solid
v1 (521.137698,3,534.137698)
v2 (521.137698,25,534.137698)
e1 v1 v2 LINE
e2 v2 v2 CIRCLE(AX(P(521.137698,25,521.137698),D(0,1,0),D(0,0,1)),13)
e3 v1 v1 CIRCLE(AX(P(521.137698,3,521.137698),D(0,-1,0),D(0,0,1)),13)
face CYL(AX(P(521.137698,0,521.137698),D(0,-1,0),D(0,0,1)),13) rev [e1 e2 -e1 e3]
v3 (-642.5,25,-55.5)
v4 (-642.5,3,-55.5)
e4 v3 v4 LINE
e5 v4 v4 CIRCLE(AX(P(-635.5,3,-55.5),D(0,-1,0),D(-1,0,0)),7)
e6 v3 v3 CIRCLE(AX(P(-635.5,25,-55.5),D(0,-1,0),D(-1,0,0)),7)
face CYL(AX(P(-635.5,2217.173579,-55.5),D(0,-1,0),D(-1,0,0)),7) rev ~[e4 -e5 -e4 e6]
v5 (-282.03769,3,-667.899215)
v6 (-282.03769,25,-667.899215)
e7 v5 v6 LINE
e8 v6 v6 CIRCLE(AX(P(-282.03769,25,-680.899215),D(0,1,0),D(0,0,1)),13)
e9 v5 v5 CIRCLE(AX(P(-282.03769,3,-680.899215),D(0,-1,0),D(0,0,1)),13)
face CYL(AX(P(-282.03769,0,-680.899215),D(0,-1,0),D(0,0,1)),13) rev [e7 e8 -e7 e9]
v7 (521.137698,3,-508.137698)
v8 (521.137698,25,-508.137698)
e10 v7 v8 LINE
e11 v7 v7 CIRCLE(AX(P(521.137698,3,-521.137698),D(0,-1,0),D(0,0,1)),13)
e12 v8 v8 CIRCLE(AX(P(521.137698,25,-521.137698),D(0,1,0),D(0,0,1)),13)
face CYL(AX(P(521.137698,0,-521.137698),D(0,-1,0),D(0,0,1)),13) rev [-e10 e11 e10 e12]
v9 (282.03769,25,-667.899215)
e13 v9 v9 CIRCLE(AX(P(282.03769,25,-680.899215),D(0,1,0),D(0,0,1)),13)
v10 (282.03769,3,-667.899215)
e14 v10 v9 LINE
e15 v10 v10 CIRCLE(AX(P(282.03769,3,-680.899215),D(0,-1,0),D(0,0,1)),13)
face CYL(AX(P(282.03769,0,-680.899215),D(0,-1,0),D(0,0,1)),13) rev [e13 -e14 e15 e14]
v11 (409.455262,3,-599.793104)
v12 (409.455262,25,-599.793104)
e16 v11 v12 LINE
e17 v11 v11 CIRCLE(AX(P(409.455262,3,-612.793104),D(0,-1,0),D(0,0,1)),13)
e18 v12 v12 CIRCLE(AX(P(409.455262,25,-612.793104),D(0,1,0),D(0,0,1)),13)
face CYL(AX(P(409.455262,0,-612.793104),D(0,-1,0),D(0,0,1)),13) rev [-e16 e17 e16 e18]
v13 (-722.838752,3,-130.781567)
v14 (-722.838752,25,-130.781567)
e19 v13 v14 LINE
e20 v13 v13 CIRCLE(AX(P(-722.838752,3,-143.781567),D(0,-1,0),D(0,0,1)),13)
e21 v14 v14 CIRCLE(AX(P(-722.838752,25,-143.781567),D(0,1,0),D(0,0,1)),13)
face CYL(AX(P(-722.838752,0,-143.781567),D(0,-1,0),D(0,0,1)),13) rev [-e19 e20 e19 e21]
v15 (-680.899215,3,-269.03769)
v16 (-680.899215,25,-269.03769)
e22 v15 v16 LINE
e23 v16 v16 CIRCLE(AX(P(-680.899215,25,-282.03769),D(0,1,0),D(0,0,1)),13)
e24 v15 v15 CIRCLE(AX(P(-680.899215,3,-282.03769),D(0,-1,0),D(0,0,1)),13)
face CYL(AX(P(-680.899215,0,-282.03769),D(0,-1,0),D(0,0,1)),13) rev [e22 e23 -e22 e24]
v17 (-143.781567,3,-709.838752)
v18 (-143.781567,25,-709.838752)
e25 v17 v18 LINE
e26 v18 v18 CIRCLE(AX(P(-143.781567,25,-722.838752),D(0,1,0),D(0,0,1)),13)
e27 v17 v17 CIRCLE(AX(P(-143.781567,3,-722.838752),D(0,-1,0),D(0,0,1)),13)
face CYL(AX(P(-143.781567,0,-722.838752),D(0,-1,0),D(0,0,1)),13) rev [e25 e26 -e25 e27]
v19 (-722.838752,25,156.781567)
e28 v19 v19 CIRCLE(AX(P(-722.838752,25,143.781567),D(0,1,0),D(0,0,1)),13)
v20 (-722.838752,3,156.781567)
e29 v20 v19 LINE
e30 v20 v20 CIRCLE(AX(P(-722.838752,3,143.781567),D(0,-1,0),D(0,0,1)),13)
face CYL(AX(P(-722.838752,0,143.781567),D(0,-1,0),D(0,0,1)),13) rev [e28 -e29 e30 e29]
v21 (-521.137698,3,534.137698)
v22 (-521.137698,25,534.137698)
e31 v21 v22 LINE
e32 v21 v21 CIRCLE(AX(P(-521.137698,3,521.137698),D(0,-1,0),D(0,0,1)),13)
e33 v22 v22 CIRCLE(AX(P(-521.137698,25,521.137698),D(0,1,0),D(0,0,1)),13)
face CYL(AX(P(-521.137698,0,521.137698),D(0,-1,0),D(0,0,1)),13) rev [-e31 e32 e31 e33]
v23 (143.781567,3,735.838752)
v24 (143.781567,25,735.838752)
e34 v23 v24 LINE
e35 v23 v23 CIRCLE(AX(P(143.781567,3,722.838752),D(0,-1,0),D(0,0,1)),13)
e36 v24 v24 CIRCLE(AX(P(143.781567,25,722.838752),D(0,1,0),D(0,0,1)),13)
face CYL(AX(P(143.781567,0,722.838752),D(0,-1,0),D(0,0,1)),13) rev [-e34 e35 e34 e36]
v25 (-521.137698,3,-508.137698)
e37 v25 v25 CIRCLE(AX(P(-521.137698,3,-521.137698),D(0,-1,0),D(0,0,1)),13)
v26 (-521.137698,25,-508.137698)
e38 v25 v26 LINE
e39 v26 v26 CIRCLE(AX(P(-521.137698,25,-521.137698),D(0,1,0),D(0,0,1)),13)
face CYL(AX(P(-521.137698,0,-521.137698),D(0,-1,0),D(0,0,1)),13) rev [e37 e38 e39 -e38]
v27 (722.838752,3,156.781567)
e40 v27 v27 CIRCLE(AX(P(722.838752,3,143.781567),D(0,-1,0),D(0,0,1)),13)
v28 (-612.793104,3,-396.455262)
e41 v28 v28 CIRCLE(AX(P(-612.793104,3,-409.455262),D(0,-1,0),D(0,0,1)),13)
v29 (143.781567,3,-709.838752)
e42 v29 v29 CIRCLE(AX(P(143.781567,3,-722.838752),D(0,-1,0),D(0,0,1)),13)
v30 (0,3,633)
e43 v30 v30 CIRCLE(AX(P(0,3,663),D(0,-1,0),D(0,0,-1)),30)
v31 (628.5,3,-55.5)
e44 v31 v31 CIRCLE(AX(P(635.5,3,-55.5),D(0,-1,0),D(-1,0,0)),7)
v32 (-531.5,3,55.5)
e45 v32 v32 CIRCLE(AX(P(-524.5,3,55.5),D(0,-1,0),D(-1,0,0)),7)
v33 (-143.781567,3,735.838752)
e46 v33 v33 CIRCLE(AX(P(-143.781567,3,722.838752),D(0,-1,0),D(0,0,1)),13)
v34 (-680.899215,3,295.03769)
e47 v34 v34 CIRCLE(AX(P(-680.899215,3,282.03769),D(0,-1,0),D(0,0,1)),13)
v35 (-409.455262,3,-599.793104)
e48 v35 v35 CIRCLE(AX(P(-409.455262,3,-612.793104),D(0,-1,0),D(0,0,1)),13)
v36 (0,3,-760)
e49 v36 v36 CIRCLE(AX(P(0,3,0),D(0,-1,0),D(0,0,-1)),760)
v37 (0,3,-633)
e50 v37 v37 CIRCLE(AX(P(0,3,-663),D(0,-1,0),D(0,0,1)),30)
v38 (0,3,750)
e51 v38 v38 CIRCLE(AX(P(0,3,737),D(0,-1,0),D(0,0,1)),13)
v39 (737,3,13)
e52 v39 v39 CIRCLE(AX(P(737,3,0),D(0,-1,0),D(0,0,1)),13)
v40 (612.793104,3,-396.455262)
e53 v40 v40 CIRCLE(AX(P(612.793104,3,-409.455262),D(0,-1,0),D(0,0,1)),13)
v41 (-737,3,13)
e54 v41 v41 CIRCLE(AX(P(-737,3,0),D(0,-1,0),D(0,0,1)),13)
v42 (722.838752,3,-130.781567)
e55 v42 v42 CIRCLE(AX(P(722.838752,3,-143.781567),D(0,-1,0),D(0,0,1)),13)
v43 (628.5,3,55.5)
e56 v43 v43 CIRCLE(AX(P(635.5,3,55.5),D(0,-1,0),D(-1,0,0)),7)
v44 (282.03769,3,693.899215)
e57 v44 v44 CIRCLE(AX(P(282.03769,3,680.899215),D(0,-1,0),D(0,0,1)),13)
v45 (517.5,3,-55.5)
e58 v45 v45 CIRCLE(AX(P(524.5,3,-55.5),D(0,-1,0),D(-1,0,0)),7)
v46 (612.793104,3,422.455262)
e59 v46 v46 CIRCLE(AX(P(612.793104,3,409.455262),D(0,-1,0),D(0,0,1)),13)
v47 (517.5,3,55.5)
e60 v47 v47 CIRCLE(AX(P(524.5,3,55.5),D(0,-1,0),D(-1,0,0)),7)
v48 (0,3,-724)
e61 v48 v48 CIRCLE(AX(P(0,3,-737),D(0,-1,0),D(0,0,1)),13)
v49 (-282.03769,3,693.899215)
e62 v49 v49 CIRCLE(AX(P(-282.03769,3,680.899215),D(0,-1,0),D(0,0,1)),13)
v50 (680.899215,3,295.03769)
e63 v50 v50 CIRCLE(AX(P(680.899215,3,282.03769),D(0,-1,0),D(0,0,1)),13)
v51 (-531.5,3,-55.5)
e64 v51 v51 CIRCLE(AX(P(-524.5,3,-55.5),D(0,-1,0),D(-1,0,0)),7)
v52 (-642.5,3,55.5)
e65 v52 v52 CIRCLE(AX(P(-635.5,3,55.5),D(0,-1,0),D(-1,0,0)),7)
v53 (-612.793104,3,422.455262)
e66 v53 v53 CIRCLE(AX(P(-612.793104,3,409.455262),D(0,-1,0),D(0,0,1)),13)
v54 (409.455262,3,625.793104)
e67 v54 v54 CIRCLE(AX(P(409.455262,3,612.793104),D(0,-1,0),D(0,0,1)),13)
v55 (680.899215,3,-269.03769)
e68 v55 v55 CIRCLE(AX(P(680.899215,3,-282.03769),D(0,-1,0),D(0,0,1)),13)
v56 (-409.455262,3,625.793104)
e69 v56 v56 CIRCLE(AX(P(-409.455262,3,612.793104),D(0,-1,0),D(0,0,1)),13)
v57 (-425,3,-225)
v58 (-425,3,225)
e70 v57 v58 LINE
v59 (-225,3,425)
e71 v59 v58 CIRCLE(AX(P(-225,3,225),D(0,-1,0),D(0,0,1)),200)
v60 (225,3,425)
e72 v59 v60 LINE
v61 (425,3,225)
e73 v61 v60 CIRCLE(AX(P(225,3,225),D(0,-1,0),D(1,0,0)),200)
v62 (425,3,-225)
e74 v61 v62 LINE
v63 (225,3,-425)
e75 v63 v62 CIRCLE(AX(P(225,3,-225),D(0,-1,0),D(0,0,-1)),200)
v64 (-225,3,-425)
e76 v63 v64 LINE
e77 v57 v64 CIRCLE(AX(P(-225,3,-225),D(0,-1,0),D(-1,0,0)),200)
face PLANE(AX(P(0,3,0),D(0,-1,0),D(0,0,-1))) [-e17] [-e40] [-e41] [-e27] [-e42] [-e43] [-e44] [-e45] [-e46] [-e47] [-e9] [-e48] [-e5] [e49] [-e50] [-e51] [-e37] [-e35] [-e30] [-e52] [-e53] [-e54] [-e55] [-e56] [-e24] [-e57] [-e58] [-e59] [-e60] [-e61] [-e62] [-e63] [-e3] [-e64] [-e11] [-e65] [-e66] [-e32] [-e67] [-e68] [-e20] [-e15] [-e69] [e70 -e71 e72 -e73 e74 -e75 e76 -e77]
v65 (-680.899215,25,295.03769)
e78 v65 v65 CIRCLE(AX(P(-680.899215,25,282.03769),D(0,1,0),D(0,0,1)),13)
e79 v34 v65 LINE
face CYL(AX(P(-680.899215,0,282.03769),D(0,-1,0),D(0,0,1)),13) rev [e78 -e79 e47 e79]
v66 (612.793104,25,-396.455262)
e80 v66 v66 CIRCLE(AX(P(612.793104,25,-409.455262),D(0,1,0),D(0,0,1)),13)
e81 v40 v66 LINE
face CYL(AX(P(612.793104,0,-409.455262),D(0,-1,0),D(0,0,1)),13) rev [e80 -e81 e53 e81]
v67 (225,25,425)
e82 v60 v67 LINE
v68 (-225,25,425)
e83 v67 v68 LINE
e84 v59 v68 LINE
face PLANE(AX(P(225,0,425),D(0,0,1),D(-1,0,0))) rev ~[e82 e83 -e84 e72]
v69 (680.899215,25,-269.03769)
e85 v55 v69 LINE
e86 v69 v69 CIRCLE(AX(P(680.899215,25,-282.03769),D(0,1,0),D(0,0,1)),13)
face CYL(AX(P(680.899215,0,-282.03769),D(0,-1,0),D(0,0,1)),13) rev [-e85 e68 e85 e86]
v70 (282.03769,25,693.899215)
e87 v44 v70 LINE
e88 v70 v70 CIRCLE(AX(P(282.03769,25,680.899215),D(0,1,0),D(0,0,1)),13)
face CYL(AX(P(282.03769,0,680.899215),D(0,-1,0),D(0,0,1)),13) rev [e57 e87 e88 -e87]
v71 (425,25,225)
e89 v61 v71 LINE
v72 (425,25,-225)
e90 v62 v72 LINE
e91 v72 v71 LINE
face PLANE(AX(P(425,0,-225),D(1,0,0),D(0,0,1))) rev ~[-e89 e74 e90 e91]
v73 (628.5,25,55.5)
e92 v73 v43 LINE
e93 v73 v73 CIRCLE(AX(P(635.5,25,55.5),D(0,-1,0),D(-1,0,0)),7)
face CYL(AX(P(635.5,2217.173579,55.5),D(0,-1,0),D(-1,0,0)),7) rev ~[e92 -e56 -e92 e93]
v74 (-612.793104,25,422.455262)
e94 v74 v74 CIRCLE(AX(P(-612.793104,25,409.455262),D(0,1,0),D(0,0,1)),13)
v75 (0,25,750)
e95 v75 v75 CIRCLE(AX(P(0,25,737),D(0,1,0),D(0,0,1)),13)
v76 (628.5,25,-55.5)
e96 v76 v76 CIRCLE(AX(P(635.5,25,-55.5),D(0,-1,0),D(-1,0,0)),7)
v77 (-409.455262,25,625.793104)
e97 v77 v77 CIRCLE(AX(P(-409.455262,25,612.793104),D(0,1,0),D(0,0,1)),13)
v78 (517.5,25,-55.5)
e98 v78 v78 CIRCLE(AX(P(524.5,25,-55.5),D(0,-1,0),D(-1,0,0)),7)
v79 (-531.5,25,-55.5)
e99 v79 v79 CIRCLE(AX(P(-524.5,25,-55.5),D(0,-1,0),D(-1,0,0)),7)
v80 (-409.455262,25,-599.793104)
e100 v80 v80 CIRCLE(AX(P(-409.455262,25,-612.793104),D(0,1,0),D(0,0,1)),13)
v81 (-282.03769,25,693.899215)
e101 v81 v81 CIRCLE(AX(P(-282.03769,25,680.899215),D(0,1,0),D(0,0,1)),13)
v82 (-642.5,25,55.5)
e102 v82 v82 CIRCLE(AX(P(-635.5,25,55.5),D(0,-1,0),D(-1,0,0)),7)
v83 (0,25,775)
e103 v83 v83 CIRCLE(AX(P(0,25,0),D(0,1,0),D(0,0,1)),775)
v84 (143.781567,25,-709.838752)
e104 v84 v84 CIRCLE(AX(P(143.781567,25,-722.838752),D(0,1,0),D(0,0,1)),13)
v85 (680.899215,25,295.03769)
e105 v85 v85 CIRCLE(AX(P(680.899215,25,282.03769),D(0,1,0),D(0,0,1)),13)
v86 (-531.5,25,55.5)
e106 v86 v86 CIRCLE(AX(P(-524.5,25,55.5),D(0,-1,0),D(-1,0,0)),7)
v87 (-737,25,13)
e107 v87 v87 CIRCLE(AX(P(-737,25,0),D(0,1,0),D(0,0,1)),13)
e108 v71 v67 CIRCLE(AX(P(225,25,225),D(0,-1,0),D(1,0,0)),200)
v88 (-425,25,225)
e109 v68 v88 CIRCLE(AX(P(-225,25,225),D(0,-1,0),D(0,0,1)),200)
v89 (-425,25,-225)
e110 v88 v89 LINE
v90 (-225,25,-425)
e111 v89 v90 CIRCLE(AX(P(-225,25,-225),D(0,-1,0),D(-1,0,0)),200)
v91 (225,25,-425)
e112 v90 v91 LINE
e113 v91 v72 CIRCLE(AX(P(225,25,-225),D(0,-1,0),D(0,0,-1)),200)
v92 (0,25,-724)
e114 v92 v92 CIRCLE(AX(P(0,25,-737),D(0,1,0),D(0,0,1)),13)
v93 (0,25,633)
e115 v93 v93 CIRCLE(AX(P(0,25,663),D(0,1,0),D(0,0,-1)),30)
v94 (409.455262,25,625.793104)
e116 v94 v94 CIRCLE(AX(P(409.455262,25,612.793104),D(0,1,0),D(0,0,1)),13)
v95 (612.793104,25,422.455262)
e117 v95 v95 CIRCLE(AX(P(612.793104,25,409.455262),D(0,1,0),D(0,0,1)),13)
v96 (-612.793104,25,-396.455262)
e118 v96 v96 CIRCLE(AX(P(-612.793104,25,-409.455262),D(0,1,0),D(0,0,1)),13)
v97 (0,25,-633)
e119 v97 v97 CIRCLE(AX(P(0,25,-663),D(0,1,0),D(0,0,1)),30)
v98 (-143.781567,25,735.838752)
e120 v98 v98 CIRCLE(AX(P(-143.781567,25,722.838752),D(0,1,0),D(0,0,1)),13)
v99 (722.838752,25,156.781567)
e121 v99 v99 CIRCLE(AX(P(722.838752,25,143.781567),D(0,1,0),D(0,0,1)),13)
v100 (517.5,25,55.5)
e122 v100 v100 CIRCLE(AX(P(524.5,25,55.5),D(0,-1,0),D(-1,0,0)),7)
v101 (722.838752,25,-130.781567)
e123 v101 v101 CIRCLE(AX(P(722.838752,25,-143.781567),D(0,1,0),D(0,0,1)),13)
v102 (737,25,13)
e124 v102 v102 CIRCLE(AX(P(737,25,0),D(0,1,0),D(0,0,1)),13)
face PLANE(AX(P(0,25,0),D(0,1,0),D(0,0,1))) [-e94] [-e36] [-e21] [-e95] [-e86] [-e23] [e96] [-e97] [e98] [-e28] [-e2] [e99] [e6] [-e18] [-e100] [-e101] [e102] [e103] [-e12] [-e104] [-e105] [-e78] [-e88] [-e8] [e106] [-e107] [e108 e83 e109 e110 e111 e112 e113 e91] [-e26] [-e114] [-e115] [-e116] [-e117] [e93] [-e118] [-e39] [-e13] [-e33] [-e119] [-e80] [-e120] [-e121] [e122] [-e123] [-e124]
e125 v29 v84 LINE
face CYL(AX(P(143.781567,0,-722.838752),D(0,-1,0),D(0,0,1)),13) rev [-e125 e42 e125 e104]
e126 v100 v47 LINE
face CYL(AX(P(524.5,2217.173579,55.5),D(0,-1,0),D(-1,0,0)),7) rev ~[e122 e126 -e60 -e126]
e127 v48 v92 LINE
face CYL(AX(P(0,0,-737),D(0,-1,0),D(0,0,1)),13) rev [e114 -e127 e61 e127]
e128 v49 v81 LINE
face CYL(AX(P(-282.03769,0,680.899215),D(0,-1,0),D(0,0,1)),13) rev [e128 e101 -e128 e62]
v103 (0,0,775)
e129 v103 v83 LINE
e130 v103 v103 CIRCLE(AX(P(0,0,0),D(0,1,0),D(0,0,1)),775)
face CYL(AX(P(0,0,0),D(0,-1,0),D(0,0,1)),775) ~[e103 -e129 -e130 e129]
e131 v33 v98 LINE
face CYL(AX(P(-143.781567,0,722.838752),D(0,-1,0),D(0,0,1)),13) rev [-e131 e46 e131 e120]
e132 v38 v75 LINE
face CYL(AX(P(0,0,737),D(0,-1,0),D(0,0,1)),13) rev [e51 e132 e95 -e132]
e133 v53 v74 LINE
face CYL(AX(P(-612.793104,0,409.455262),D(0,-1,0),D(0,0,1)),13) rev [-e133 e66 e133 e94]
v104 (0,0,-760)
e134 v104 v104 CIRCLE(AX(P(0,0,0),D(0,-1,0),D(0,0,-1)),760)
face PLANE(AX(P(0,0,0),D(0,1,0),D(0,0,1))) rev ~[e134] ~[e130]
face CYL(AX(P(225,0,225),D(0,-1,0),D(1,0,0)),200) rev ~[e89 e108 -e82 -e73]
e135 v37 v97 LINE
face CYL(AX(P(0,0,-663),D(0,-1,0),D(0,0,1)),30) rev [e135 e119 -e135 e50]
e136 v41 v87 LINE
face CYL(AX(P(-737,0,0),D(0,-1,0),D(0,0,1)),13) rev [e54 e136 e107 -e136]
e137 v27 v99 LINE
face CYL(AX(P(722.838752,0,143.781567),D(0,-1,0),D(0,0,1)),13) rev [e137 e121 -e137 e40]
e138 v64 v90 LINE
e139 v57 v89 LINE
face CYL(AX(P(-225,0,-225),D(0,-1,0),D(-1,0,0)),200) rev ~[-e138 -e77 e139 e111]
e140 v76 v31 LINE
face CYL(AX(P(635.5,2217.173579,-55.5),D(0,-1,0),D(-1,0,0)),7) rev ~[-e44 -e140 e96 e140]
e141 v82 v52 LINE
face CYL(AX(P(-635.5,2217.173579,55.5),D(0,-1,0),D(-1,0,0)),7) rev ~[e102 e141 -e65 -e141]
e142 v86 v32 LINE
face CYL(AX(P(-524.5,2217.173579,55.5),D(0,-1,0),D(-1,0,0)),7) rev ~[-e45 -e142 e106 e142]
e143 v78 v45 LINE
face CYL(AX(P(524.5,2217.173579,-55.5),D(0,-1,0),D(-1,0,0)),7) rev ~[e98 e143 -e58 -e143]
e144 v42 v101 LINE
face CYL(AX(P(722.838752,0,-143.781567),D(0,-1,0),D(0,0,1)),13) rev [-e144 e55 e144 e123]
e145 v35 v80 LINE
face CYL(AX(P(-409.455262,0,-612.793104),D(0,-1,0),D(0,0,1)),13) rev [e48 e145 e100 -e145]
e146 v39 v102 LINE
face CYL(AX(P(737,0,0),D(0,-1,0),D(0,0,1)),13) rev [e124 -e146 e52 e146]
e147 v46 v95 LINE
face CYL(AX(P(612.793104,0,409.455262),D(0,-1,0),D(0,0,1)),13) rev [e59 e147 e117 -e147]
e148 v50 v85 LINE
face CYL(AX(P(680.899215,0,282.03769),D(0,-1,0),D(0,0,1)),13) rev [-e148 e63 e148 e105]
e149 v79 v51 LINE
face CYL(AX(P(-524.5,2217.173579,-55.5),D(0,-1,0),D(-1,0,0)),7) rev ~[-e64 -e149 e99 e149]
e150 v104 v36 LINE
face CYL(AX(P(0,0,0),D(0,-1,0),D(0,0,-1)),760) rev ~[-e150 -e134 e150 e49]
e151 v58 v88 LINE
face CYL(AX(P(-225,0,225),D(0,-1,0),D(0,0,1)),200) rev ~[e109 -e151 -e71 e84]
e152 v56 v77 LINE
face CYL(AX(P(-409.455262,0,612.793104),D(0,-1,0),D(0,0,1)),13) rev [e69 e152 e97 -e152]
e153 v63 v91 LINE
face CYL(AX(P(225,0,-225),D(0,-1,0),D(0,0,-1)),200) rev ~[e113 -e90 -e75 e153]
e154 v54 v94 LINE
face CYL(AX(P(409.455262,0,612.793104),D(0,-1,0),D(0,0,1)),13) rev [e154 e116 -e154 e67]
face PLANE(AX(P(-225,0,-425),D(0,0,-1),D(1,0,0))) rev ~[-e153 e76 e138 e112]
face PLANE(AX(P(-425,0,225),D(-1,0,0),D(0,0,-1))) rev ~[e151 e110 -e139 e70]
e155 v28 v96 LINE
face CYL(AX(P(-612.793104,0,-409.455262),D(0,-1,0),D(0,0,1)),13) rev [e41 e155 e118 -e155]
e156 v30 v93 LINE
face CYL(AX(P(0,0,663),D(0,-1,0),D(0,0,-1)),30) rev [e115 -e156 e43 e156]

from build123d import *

# Parameters (mm, degrees)
SKETCH1_R           = 775
SKETCH1_R_2         = 30
SKETCH1_R_3         = 13
BOSS_EXTRUDE1_DEPTH = 25
M16_TAPPED_HOLE1_D  = 14
SKETCH4_R           = 760
CUT_EXTRUDE1_DEPTH  = 3


with BuildPart() as part:
    # Sketch1 → Boss-Extrude1 (new body)
    with BuildSketch(Plane(origin=(0, 0, 0), x_dir=(1, 0, 0), z_dir=(0, 1, 0))):
        with Locations(Location((0, 0, 0), (0, 0, 270))):
            Circle(SKETCH1_R)
        with Locations(Location((0, 663, 0), (0, 0, 270))):
            Circle(SKETCH1_R_2, mode=Mode.SUBTRACT)
        with Locations(Location((0, -663, 0), (0, 0, 90))):
            Circle(SKETCH1_R_2, mode=Mode.SUBTRACT)
        with Locations(Location((0, 737, 0), (0, 0, 270))):
            Circle(SKETCH1_R_3, mode=Mode.SUBTRACT)
        with Locations(Location((143.781567326, 722.838751657, 0), (0, 0, 270))):
            Circle(SKETCH1_R_3, mode=Mode.SUBTRACT)
        with Locations(Location((282.037689653, 680.899215461, 0), (0, 0, 270))):
            Circle(SKETCH1_R_3, mode=Mode.SUBTRACT)
        with Locations(Location((409.455261735, 612.793104267, 0), (0, 0, 270))):
            Circle(SKETCH1_R_3, mode=Mode.SUBTRACT)
        with Locations(Location((521.137697734, 521.137697734, 0), (0, 0, 270))):
            Circle(SKETCH1_R_3, mode=Mode.SUBTRACT)
        with Locations(Location((612.793104267, 409.455261735, 0), (0, 0, 270))):
            Circle(SKETCH1_R_3, mode=Mode.SUBTRACT)
        with Locations(Location((680.899215461, 282.037689653, 0), (0, 0, 270))):
            Circle(SKETCH1_R_3, mode=Mode.SUBTRACT)
        with Locations(Location((722.838751657, 143.781567326, 0), (0, 0, 270))):
            Circle(SKETCH1_R_3, mode=Mode.SUBTRACT)
        with Locations(Location((737, 0, 0), (0, 0, 270))):
            Circle(SKETCH1_R_3, mode=Mode.SUBTRACT)
        with Locations(Location((722.838751657, -143.781567326, 0), (0, 0, 270))):
            Circle(SKETCH1_R_3, mode=Mode.SUBTRACT)
        with Locations(Location((680.899215461, -282.037689653, 0), (0, 0, 270))):
            Circle(SKETCH1_R_3, mode=Mode.SUBTRACT)
        with Locations(Location((612.793104267, -409.455261735, 0), (0, 0, 270))):
            Circle(SKETCH1_R_3, mode=Mode.SUBTRACT)
        with Locations(Location((521.137697734, -521.137697734, 0), (0, 0, 270))):
            Circle(SKETCH1_R_3, mode=Mode.SUBTRACT)
        with Locations(Location((409.455261735, -612.793104267, 0), (0, 0, 270))):
            Circle(SKETCH1_R_3, mode=Mode.SUBTRACT)
        with Locations(Location((282.037689653, -680.899215461, 0), (0, 0, 270))):
            Circle(SKETCH1_R_3, mode=Mode.SUBTRACT)
        with Locations(Location((143.781567326, -722.838751657, 0), (0, 0, 270))):
            Circle(SKETCH1_R_3, mode=Mode.SUBTRACT)
        with Locations(Location((0, -737, 0), (0, 0, 270))):
            Circle(SKETCH1_R_3, mode=Mode.SUBTRACT)
        with Locations(Location((-143.781567326, -722.838751657, 0), (0, 0, 270))):
            Circle(SKETCH1_R_3, mode=Mode.SUBTRACT)
        with Locations(Location((-282.037689653, -680.899215461, 0), (0, 0, 270))):
            Circle(SKETCH1_R_3, mode=Mode.SUBTRACT)
        with Locations(Location((-409.455261735, -612.793104267, 0), (0, 0, 270))):
            Circle(SKETCH1_R_3, mode=Mode.SUBTRACT)
        with Locations(Location((-521.137697734, -521.137697734, 0), (0, 0, 270))):
            Circle(SKETCH1_R_3, mode=Mode.SUBTRACT)
        with Locations(Location((-612.793104267, -409.455261735, 0), (0, 0, 270))):
            Circle(SKETCH1_R_3, mode=Mode.SUBTRACT)
        with Locations(Location((-680.899215461, -282.037689653, 0), (0, 0, 270))):
            Circle(SKETCH1_R_3, mode=Mode.SUBTRACT)
        with Locations(Location((-722.838751657, -143.781567326, 0), (0, 0, 270))):
            Circle(SKETCH1_R_3, mode=Mode.SUBTRACT)
        with Locations(Location((-737, 0, 0), (0, 0, 270))):
            Circle(SKETCH1_R_3, mode=Mode.SUBTRACT)
        with Locations(Location((-722.838751657, 143.781567326, 0), (0, 0, 270))):
            Circle(SKETCH1_R_3, mode=Mode.SUBTRACT)
        with Locations(Location((-680.899215461, 282.037689653, 0), (0, 0, 270))):
            Circle(SKETCH1_R_3, mode=Mode.SUBTRACT)
        with Locations(Location((-612.793104267, 409.455261735, 0), (0, 0, 270))):
            Circle(SKETCH1_R_3, mode=Mode.SUBTRACT)
        with Locations(Location((-521.137697734, 521.137697734, 0), (0, 0, 270))):
            Circle(SKETCH1_R_3, mode=Mode.SUBTRACT)
        with Locations(Location((-409.455261735, 612.793104267, 0), (0, 0, 270))):
            Circle(SKETCH1_R_3, mode=Mode.SUBTRACT)
        with Locations(Location((-282.037689653, 680.899215461, 0), (0, 0, 270))):
            Circle(SKETCH1_R_3, mode=Mode.SUBTRACT)
        with Locations(Location((-143.781567326, 722.838751657, 0), (0, 0, 270))):
            Circle(SKETCH1_R_3, mode=Mode.SUBTRACT)
        with BuildLine():
            Line((225, -425), (-225, -425))
            ThreePointArc((-225, -425), (-366.421356237, -366.421356237), (-425, -225))
            Line((-425, -225), (-425, 225))
            ThreePointArc((-425, 225), (-366.421356237, 366.421356237), (-225, 425))
            Line((-225, 425), (225, 425))
            ThreePointArc((225, 425), (366.421356237, 366.421356237), (425, 225))
            Line((425, 225), (425, -225))
            ThreePointArc((425, -225), (366.421356237, -366.421356237), (225, -425))
        make_face(mode=Mode.SUBTRACT)
    extrude(amount=BOSS_EXTRUDE1_DEPTH)

    # M16 Tapped Hole1 (through all)
    with Locations(Plane(origin=(0, 25, 0), x_dir=(1, 0, 0), z_dir=(0, 1, 0))):
        with Locations((-635.5, -55.5), (-524.5, -55.5), (-524.5, 55.5), (-635.5, 55.5), (635.5, 55.5), (524.5, 55.5), (524.5, -55.5), (635.5, -55.5)):
            Hole(M16_TAPPED_HOLE1_D / 2)

    # Sketch4 → Cut-Extrude1 (cut)
    with BuildSketch(Plane.XZ):
        with Locations(Location((0, 0, 0), (0, 0, 270))):
            Circle(SKETCH4_R)
    extrude(amount=-CUT_EXTRUDE1_DEPTH, mode=Mode.SUBTRACT)


solid = part.part
